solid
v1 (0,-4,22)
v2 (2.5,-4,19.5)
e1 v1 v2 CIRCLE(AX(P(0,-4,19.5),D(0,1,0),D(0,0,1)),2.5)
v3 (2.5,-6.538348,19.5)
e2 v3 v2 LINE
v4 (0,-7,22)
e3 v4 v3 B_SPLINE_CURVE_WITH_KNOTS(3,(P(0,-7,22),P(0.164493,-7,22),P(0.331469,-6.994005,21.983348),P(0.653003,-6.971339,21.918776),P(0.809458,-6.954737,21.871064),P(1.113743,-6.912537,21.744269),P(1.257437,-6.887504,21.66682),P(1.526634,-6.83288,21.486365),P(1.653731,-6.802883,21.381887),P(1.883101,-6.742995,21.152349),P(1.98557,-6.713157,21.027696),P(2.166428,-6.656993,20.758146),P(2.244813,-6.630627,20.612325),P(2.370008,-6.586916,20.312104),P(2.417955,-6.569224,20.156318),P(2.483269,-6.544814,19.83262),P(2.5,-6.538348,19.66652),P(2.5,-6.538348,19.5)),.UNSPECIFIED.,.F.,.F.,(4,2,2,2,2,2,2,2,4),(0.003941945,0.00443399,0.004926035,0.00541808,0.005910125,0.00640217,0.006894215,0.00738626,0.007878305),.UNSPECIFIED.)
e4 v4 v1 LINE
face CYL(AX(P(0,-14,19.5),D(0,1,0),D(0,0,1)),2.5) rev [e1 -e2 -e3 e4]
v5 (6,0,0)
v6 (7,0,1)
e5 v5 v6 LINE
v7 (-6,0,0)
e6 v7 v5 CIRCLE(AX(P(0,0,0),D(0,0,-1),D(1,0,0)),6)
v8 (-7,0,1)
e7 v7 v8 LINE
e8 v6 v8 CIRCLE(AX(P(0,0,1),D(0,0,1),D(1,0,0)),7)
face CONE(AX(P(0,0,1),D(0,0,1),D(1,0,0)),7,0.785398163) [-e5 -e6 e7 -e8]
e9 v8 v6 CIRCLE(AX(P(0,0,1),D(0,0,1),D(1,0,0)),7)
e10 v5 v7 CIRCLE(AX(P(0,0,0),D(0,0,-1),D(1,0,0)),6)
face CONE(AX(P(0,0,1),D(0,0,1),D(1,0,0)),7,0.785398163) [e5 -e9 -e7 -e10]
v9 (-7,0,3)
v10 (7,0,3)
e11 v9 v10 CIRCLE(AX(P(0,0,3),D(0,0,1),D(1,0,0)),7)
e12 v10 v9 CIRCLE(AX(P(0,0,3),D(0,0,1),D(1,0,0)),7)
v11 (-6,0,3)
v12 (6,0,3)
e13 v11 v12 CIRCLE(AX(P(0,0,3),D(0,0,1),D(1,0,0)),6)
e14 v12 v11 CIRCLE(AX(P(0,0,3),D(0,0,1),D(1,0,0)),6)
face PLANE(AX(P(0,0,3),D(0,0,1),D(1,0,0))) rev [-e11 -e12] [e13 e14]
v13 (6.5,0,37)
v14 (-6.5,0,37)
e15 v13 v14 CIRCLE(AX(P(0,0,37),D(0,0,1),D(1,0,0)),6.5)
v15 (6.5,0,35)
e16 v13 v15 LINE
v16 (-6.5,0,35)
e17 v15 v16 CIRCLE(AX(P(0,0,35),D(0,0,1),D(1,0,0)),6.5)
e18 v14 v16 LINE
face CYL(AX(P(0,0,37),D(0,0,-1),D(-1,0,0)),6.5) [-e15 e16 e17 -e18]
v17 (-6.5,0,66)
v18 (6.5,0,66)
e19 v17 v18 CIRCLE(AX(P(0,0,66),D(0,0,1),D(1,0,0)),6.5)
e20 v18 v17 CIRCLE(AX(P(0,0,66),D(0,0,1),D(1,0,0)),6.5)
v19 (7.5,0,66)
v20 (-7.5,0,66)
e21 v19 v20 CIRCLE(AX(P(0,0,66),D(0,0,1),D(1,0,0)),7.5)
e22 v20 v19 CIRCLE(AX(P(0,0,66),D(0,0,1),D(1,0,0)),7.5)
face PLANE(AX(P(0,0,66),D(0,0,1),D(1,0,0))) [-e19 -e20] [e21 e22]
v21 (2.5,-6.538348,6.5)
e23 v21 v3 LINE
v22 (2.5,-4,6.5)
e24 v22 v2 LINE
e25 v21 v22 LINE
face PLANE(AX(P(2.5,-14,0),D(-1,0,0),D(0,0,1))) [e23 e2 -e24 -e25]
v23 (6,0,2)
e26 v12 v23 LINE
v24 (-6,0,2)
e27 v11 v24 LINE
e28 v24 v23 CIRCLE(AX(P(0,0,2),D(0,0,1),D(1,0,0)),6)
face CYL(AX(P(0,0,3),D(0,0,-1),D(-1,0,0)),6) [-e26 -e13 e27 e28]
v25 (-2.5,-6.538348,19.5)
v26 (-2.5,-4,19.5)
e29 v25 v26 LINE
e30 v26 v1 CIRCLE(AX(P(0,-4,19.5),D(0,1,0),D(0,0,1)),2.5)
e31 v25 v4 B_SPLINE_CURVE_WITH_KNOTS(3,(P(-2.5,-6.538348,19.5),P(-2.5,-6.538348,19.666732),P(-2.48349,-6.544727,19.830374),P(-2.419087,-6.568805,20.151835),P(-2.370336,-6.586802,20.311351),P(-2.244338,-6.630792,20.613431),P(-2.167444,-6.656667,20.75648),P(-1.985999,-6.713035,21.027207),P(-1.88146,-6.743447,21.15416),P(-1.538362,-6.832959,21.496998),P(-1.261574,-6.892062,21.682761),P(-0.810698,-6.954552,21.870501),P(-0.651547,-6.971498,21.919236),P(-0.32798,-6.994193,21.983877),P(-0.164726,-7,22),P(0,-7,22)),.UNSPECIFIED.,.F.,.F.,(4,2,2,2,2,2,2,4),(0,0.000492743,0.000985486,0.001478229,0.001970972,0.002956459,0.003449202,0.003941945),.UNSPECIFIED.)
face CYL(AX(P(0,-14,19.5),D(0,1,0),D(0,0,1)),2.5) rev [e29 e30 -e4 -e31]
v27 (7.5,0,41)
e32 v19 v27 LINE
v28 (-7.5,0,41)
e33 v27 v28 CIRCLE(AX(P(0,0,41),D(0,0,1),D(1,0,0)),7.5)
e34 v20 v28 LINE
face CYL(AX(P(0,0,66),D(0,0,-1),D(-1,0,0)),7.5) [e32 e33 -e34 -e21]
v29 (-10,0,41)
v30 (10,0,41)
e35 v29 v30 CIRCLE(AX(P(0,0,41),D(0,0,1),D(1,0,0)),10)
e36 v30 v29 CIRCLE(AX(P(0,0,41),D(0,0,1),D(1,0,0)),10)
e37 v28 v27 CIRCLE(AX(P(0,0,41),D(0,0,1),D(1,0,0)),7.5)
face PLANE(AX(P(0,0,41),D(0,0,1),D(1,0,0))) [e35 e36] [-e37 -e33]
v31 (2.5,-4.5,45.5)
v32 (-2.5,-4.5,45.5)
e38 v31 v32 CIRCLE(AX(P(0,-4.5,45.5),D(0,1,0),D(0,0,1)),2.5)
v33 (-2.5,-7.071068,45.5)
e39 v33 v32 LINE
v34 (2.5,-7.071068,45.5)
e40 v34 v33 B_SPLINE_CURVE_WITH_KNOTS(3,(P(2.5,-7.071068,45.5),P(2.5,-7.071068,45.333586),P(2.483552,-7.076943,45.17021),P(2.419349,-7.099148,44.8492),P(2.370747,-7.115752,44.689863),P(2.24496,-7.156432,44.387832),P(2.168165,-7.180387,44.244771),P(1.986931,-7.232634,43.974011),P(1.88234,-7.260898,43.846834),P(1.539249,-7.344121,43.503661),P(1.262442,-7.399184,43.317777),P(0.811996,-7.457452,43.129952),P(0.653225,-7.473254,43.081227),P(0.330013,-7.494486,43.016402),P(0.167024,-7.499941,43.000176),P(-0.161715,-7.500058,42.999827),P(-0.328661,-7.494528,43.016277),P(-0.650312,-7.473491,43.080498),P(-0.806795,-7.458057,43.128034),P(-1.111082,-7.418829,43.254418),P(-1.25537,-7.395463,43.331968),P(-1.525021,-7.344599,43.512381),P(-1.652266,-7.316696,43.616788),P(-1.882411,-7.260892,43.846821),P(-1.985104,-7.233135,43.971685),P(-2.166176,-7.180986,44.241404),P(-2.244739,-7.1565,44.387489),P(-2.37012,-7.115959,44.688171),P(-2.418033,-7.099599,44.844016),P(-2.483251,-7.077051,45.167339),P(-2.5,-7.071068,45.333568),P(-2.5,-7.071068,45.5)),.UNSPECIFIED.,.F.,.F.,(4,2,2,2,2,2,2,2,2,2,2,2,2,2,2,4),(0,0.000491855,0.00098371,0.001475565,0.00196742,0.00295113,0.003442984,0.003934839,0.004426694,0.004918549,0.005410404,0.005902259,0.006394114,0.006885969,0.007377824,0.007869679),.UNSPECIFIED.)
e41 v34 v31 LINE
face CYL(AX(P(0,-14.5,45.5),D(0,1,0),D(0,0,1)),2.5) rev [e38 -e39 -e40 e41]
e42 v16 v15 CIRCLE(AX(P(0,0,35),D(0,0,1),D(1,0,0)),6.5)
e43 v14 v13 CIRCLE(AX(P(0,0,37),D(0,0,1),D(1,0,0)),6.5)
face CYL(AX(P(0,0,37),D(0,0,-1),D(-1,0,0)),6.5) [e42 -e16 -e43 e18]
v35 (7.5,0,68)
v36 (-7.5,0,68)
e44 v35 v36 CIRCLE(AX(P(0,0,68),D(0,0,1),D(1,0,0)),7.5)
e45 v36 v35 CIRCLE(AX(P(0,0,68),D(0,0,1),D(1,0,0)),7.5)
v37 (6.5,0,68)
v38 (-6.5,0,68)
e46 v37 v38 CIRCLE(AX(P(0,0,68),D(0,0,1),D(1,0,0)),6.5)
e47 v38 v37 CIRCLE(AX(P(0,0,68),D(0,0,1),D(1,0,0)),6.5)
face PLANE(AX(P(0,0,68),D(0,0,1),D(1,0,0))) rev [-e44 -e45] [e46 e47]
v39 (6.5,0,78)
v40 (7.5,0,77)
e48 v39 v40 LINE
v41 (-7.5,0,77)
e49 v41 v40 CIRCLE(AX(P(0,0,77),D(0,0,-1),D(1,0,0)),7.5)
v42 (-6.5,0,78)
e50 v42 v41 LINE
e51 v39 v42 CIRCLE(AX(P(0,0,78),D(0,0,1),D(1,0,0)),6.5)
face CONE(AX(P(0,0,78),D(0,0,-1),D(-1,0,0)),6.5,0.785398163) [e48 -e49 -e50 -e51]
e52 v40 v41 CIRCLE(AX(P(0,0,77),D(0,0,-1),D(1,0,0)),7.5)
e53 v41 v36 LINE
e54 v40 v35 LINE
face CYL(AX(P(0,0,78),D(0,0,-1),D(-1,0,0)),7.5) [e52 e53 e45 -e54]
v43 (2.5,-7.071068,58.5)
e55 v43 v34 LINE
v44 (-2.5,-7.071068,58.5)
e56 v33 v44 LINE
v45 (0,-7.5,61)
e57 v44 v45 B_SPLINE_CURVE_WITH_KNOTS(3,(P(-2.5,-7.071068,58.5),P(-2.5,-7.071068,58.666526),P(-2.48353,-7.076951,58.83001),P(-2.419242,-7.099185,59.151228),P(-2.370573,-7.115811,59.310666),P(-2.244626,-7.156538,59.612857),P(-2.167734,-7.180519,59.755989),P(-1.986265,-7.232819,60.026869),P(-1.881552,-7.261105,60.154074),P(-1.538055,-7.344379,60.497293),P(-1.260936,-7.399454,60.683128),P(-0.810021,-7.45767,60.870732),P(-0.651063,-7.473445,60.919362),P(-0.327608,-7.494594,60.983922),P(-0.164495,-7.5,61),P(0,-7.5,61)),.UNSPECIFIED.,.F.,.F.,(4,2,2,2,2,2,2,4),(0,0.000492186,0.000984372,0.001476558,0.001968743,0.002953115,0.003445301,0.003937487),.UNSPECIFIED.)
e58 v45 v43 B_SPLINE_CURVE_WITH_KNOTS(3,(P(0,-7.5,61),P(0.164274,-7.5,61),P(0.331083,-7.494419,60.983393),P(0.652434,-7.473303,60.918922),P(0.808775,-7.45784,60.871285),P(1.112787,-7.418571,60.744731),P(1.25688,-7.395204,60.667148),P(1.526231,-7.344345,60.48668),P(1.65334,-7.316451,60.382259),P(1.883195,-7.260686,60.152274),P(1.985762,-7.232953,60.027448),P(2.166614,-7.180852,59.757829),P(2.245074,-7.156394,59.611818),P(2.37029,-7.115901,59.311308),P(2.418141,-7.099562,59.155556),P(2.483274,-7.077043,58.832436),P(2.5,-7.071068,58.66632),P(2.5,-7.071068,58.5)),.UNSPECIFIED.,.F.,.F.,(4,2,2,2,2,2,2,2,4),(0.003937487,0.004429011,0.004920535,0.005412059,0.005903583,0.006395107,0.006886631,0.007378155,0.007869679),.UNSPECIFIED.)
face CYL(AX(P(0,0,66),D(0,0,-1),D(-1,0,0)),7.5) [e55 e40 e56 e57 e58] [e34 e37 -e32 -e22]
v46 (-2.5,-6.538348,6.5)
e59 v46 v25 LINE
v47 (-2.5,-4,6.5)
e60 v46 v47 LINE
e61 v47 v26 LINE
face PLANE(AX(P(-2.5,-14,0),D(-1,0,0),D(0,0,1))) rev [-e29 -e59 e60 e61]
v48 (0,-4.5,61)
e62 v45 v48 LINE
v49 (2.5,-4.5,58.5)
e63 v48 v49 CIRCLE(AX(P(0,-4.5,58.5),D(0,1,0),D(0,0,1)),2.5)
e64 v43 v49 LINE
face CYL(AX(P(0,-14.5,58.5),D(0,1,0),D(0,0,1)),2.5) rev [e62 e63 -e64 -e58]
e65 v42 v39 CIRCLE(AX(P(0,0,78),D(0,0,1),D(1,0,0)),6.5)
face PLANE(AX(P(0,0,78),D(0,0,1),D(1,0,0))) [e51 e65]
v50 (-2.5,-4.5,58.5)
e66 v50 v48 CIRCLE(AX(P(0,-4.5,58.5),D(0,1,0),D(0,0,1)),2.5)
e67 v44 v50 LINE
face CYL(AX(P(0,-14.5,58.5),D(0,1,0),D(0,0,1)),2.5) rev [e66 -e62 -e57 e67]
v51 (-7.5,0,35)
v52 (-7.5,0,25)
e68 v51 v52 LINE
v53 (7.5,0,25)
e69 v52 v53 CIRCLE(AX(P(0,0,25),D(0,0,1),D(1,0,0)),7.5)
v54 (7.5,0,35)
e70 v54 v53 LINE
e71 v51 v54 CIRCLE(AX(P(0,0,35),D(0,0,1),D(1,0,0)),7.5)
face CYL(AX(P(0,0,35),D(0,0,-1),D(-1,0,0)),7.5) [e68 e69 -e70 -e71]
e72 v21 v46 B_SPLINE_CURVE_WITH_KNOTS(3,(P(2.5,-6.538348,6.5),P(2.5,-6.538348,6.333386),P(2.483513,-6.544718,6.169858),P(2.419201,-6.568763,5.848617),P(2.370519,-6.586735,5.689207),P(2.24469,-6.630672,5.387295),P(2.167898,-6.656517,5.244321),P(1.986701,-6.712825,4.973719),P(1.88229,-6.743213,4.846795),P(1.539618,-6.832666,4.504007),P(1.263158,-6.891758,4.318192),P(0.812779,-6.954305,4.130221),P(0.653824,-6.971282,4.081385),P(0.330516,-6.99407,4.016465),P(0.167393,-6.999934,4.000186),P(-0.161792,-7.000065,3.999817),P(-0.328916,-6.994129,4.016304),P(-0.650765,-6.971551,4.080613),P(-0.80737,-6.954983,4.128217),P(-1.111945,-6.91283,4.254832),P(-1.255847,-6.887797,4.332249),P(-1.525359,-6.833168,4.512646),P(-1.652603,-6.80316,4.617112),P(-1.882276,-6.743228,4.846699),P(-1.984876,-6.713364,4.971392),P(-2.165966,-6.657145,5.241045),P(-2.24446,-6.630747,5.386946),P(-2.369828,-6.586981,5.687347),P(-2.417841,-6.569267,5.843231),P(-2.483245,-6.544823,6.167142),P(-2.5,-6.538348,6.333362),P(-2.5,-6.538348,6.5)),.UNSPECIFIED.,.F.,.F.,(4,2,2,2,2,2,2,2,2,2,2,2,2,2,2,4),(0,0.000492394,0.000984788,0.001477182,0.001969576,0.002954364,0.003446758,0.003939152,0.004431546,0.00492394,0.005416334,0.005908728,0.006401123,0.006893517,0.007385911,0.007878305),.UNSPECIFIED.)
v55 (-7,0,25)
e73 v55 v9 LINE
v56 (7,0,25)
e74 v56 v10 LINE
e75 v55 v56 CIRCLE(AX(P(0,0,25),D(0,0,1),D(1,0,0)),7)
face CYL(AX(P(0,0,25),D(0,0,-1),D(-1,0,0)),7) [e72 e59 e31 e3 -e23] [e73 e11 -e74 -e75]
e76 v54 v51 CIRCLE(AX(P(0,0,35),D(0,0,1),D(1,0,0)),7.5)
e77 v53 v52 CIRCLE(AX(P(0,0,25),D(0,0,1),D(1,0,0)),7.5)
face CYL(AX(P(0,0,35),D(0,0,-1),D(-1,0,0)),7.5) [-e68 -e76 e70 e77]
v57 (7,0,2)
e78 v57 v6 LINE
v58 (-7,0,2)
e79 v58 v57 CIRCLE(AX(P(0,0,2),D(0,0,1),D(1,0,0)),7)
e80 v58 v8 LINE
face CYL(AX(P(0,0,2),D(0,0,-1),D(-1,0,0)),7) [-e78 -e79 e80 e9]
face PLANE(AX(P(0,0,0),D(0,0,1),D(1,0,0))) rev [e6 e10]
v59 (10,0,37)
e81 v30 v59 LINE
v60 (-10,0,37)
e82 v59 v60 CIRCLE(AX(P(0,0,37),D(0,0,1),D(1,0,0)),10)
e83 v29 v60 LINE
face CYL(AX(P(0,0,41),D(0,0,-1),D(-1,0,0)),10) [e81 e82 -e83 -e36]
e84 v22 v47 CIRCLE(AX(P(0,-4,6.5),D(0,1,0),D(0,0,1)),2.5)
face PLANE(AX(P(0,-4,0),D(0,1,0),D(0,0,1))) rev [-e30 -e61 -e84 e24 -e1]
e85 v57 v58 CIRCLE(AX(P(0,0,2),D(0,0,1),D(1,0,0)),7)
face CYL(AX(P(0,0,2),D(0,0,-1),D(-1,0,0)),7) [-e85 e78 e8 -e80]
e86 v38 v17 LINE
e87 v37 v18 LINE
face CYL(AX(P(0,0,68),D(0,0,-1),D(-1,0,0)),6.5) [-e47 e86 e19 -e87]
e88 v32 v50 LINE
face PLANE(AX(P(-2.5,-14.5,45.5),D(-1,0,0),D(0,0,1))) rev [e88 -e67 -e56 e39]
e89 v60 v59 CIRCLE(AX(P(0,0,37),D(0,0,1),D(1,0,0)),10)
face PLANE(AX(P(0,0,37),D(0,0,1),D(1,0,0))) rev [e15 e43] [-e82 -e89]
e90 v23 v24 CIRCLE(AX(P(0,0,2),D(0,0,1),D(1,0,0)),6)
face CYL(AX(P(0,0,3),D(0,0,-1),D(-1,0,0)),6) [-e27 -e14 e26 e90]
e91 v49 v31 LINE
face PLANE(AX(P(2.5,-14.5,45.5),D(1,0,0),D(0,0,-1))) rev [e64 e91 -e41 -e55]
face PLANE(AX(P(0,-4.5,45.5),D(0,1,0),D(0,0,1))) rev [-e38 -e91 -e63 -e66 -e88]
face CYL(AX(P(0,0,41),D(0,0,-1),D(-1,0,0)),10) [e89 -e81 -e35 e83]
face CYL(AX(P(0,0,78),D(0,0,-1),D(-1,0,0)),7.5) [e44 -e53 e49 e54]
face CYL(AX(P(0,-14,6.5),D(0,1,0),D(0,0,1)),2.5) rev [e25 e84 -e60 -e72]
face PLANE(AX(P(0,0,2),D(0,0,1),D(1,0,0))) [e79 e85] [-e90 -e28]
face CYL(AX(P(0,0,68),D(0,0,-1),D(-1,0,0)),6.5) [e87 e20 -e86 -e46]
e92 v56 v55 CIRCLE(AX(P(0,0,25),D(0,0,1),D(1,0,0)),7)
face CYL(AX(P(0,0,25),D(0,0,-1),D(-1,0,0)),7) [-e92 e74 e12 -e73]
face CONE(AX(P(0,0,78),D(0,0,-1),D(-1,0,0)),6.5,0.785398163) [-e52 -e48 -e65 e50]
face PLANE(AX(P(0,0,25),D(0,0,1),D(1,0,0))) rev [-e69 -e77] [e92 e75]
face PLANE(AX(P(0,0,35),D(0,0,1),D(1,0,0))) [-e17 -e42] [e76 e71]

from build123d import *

# Parameters (mm, degrees)
SKETCH2_R           = 7
BOSS_EXTRUDE1_DEPTH = 2
SKETCH3_R           = 6
BOSS_EXTRUDE2_DEPTH = 1
SKETCH4_R           = 7
BOSS_EXTRUDE3_DEPTH = 22
SKETCH5_R           = 7.5
BOSS_EXTRUDE4_DEPTH = 10
SKETCH6_R           = 6.5
BOSS_EXTRUDE5_DEPTH = 2
SKETCH7_R           = 10
BOSS_EXTRUDE6_DEPTH = 4
SKETCH8_R           = 7.5
BOSS_EXTRUDE7_DEPTH = 25
SKETCH9_R           = 6.5
BOSS_EXTRUDE8_DEPTH = 2
SKETCH10_R          = 7.5
BOSS_EXTRUDE9_DEPTH = 10
CHAMFER1_SIZE       = 1
CUT_EXTRUDE1_START  = -4
CUT_EXTRUDE1_DEPTH  = 10
CUT_EXTRUDE2_START  = -4.5
CUT_EXTRUDE2_DEPTH  = 10


with BuildPart() as part:
    # Sketch2 → Boss-Extrude1 (new body)
    with BuildSketch(Plane.XY):
        Circle(SKETCH2_R)
    extrude(amount=BOSS_EXTRUDE1_DEPTH)

    # Sketch3 → Boss-Extrude2 (add)
    with BuildSketch(Plane.XY.offset(2)):
        Circle(SKETCH3_R)
    extrude(amount=BOSS_EXTRUDE2_DEPTH)

    # Sketch4 → Boss-Extrude3 (add)
    with BuildSketch(Plane.XY.offset(3)):
        Circle(SKETCH4_R)
    extrude(amount=BOSS_EXTRUDE3_DEPTH)

    # Sketch5 → Boss-Extrude4 (add)
    with BuildSketch(Plane.XY.offset(25)):
        Circle(SKETCH5_R)
    extrude(amount=BOSS_EXTRUDE4_DEPTH)

    # Sketch6 → Boss-Extrude5 (add)
    with BuildSketch(Plane.XY.offset(35)):
        Circle(SKETCH6_R)
    extrude(amount=BOSS_EXTRUDE5_DEPTH)

    # Sketch7 → Boss-Extrude6 (add)
    with BuildSketch(Plane.XY.offset(37)):
        Circle(SKETCH7_R)
    extrude(amount=BOSS_EXTRUDE6_DEPTH)

    # Sketch8 → Boss-Extrude7 (add)
    with BuildSketch(Plane.XY.offset(41)):
        Circle(SKETCH8_R)
    extrude(amount=BOSS_EXTRUDE7_DEPTH)

    # Sketch9 → Boss-Extrude8 (add)
    with BuildSketch(Plane.XY.offset(66)):
        Circle(SKETCH9_R)
    extrude(amount=BOSS_EXTRUDE8_DEPTH)

    # Sketch10 → Boss-Extrude9 (add)
    with BuildSketch(Plane.XY.offset(68)):
        Circle(SKETCH10_R)
    extrude(amount=BOSS_EXTRUDE9_DEPTH)

    # Chamfer1
    chamfer1_edges = [part.edges().sort_by_distance(p)[0] for p in [
        (-7, 0, 0),
        (-7.5, 0, 78),
    ]]
    chamfer(chamfer1_edges, length=CHAMFER1_SIZE)

    # Sketch11 → Cut-Extrude1 (cut)
    with BuildSketch(Plane(origin=(0, 0, 0), x_dir=(1, 0, 0), z_dir=(0, 1, 0)).offset(CUT_EXTRUDE1_START)):
        with BuildLine():
            ThreePointArc((2.5, -6.5), (1.767766953, -4.732233047), (0, -4))
            Line((0, -4), (0, -22))
            ThreePointArc((0, -22), (1.767766953, -21.267766953), (2.5, -19.5))
            Line((2.5, -19.5), (2.5, -6.5))
        make_face()
        with BuildLine():
            Line((0, -22), (0, -4))
            ThreePointArc((0, -4), (-1.767766953, -4.732233047), (-2.5, -6.5))
            Line((-2.5, -6.5), (-2.5, -19.5))
            ThreePointArc((-2.5, -19.5), (-1.767766953, -21.267766953), (0, -22))
        make_face()
    extrude(amount=-CUT_EXTRUDE1_DEPTH, mode=Mode.SUBTRACT)

    # Sketch12 → Cut-Extrude2 (cut)
    with BuildSketch(Plane(origin=(0, 0, 0), x_dir=(1, 0, 0), z_dir=(0, 1, 0)).offset(CUT_EXTRUDE2_START)):
        with BuildLine():
            Line((2.5, -45.5), (2.5, -58.5))
            ThreePointArc((2.5, -58.5), (0, -61), (-2.5, -58.5))
            Line((-2.5, -58.5), (-2.5, -45.5))
            ThreePointArc((-2.5, -45.5), (0, -43), (2.5, -45.5))
        make_face()
    extrude(amount=-CUT_EXTRUDE2_DEPTH, mode=Mode.SUBTRACT)


solid = part.part
